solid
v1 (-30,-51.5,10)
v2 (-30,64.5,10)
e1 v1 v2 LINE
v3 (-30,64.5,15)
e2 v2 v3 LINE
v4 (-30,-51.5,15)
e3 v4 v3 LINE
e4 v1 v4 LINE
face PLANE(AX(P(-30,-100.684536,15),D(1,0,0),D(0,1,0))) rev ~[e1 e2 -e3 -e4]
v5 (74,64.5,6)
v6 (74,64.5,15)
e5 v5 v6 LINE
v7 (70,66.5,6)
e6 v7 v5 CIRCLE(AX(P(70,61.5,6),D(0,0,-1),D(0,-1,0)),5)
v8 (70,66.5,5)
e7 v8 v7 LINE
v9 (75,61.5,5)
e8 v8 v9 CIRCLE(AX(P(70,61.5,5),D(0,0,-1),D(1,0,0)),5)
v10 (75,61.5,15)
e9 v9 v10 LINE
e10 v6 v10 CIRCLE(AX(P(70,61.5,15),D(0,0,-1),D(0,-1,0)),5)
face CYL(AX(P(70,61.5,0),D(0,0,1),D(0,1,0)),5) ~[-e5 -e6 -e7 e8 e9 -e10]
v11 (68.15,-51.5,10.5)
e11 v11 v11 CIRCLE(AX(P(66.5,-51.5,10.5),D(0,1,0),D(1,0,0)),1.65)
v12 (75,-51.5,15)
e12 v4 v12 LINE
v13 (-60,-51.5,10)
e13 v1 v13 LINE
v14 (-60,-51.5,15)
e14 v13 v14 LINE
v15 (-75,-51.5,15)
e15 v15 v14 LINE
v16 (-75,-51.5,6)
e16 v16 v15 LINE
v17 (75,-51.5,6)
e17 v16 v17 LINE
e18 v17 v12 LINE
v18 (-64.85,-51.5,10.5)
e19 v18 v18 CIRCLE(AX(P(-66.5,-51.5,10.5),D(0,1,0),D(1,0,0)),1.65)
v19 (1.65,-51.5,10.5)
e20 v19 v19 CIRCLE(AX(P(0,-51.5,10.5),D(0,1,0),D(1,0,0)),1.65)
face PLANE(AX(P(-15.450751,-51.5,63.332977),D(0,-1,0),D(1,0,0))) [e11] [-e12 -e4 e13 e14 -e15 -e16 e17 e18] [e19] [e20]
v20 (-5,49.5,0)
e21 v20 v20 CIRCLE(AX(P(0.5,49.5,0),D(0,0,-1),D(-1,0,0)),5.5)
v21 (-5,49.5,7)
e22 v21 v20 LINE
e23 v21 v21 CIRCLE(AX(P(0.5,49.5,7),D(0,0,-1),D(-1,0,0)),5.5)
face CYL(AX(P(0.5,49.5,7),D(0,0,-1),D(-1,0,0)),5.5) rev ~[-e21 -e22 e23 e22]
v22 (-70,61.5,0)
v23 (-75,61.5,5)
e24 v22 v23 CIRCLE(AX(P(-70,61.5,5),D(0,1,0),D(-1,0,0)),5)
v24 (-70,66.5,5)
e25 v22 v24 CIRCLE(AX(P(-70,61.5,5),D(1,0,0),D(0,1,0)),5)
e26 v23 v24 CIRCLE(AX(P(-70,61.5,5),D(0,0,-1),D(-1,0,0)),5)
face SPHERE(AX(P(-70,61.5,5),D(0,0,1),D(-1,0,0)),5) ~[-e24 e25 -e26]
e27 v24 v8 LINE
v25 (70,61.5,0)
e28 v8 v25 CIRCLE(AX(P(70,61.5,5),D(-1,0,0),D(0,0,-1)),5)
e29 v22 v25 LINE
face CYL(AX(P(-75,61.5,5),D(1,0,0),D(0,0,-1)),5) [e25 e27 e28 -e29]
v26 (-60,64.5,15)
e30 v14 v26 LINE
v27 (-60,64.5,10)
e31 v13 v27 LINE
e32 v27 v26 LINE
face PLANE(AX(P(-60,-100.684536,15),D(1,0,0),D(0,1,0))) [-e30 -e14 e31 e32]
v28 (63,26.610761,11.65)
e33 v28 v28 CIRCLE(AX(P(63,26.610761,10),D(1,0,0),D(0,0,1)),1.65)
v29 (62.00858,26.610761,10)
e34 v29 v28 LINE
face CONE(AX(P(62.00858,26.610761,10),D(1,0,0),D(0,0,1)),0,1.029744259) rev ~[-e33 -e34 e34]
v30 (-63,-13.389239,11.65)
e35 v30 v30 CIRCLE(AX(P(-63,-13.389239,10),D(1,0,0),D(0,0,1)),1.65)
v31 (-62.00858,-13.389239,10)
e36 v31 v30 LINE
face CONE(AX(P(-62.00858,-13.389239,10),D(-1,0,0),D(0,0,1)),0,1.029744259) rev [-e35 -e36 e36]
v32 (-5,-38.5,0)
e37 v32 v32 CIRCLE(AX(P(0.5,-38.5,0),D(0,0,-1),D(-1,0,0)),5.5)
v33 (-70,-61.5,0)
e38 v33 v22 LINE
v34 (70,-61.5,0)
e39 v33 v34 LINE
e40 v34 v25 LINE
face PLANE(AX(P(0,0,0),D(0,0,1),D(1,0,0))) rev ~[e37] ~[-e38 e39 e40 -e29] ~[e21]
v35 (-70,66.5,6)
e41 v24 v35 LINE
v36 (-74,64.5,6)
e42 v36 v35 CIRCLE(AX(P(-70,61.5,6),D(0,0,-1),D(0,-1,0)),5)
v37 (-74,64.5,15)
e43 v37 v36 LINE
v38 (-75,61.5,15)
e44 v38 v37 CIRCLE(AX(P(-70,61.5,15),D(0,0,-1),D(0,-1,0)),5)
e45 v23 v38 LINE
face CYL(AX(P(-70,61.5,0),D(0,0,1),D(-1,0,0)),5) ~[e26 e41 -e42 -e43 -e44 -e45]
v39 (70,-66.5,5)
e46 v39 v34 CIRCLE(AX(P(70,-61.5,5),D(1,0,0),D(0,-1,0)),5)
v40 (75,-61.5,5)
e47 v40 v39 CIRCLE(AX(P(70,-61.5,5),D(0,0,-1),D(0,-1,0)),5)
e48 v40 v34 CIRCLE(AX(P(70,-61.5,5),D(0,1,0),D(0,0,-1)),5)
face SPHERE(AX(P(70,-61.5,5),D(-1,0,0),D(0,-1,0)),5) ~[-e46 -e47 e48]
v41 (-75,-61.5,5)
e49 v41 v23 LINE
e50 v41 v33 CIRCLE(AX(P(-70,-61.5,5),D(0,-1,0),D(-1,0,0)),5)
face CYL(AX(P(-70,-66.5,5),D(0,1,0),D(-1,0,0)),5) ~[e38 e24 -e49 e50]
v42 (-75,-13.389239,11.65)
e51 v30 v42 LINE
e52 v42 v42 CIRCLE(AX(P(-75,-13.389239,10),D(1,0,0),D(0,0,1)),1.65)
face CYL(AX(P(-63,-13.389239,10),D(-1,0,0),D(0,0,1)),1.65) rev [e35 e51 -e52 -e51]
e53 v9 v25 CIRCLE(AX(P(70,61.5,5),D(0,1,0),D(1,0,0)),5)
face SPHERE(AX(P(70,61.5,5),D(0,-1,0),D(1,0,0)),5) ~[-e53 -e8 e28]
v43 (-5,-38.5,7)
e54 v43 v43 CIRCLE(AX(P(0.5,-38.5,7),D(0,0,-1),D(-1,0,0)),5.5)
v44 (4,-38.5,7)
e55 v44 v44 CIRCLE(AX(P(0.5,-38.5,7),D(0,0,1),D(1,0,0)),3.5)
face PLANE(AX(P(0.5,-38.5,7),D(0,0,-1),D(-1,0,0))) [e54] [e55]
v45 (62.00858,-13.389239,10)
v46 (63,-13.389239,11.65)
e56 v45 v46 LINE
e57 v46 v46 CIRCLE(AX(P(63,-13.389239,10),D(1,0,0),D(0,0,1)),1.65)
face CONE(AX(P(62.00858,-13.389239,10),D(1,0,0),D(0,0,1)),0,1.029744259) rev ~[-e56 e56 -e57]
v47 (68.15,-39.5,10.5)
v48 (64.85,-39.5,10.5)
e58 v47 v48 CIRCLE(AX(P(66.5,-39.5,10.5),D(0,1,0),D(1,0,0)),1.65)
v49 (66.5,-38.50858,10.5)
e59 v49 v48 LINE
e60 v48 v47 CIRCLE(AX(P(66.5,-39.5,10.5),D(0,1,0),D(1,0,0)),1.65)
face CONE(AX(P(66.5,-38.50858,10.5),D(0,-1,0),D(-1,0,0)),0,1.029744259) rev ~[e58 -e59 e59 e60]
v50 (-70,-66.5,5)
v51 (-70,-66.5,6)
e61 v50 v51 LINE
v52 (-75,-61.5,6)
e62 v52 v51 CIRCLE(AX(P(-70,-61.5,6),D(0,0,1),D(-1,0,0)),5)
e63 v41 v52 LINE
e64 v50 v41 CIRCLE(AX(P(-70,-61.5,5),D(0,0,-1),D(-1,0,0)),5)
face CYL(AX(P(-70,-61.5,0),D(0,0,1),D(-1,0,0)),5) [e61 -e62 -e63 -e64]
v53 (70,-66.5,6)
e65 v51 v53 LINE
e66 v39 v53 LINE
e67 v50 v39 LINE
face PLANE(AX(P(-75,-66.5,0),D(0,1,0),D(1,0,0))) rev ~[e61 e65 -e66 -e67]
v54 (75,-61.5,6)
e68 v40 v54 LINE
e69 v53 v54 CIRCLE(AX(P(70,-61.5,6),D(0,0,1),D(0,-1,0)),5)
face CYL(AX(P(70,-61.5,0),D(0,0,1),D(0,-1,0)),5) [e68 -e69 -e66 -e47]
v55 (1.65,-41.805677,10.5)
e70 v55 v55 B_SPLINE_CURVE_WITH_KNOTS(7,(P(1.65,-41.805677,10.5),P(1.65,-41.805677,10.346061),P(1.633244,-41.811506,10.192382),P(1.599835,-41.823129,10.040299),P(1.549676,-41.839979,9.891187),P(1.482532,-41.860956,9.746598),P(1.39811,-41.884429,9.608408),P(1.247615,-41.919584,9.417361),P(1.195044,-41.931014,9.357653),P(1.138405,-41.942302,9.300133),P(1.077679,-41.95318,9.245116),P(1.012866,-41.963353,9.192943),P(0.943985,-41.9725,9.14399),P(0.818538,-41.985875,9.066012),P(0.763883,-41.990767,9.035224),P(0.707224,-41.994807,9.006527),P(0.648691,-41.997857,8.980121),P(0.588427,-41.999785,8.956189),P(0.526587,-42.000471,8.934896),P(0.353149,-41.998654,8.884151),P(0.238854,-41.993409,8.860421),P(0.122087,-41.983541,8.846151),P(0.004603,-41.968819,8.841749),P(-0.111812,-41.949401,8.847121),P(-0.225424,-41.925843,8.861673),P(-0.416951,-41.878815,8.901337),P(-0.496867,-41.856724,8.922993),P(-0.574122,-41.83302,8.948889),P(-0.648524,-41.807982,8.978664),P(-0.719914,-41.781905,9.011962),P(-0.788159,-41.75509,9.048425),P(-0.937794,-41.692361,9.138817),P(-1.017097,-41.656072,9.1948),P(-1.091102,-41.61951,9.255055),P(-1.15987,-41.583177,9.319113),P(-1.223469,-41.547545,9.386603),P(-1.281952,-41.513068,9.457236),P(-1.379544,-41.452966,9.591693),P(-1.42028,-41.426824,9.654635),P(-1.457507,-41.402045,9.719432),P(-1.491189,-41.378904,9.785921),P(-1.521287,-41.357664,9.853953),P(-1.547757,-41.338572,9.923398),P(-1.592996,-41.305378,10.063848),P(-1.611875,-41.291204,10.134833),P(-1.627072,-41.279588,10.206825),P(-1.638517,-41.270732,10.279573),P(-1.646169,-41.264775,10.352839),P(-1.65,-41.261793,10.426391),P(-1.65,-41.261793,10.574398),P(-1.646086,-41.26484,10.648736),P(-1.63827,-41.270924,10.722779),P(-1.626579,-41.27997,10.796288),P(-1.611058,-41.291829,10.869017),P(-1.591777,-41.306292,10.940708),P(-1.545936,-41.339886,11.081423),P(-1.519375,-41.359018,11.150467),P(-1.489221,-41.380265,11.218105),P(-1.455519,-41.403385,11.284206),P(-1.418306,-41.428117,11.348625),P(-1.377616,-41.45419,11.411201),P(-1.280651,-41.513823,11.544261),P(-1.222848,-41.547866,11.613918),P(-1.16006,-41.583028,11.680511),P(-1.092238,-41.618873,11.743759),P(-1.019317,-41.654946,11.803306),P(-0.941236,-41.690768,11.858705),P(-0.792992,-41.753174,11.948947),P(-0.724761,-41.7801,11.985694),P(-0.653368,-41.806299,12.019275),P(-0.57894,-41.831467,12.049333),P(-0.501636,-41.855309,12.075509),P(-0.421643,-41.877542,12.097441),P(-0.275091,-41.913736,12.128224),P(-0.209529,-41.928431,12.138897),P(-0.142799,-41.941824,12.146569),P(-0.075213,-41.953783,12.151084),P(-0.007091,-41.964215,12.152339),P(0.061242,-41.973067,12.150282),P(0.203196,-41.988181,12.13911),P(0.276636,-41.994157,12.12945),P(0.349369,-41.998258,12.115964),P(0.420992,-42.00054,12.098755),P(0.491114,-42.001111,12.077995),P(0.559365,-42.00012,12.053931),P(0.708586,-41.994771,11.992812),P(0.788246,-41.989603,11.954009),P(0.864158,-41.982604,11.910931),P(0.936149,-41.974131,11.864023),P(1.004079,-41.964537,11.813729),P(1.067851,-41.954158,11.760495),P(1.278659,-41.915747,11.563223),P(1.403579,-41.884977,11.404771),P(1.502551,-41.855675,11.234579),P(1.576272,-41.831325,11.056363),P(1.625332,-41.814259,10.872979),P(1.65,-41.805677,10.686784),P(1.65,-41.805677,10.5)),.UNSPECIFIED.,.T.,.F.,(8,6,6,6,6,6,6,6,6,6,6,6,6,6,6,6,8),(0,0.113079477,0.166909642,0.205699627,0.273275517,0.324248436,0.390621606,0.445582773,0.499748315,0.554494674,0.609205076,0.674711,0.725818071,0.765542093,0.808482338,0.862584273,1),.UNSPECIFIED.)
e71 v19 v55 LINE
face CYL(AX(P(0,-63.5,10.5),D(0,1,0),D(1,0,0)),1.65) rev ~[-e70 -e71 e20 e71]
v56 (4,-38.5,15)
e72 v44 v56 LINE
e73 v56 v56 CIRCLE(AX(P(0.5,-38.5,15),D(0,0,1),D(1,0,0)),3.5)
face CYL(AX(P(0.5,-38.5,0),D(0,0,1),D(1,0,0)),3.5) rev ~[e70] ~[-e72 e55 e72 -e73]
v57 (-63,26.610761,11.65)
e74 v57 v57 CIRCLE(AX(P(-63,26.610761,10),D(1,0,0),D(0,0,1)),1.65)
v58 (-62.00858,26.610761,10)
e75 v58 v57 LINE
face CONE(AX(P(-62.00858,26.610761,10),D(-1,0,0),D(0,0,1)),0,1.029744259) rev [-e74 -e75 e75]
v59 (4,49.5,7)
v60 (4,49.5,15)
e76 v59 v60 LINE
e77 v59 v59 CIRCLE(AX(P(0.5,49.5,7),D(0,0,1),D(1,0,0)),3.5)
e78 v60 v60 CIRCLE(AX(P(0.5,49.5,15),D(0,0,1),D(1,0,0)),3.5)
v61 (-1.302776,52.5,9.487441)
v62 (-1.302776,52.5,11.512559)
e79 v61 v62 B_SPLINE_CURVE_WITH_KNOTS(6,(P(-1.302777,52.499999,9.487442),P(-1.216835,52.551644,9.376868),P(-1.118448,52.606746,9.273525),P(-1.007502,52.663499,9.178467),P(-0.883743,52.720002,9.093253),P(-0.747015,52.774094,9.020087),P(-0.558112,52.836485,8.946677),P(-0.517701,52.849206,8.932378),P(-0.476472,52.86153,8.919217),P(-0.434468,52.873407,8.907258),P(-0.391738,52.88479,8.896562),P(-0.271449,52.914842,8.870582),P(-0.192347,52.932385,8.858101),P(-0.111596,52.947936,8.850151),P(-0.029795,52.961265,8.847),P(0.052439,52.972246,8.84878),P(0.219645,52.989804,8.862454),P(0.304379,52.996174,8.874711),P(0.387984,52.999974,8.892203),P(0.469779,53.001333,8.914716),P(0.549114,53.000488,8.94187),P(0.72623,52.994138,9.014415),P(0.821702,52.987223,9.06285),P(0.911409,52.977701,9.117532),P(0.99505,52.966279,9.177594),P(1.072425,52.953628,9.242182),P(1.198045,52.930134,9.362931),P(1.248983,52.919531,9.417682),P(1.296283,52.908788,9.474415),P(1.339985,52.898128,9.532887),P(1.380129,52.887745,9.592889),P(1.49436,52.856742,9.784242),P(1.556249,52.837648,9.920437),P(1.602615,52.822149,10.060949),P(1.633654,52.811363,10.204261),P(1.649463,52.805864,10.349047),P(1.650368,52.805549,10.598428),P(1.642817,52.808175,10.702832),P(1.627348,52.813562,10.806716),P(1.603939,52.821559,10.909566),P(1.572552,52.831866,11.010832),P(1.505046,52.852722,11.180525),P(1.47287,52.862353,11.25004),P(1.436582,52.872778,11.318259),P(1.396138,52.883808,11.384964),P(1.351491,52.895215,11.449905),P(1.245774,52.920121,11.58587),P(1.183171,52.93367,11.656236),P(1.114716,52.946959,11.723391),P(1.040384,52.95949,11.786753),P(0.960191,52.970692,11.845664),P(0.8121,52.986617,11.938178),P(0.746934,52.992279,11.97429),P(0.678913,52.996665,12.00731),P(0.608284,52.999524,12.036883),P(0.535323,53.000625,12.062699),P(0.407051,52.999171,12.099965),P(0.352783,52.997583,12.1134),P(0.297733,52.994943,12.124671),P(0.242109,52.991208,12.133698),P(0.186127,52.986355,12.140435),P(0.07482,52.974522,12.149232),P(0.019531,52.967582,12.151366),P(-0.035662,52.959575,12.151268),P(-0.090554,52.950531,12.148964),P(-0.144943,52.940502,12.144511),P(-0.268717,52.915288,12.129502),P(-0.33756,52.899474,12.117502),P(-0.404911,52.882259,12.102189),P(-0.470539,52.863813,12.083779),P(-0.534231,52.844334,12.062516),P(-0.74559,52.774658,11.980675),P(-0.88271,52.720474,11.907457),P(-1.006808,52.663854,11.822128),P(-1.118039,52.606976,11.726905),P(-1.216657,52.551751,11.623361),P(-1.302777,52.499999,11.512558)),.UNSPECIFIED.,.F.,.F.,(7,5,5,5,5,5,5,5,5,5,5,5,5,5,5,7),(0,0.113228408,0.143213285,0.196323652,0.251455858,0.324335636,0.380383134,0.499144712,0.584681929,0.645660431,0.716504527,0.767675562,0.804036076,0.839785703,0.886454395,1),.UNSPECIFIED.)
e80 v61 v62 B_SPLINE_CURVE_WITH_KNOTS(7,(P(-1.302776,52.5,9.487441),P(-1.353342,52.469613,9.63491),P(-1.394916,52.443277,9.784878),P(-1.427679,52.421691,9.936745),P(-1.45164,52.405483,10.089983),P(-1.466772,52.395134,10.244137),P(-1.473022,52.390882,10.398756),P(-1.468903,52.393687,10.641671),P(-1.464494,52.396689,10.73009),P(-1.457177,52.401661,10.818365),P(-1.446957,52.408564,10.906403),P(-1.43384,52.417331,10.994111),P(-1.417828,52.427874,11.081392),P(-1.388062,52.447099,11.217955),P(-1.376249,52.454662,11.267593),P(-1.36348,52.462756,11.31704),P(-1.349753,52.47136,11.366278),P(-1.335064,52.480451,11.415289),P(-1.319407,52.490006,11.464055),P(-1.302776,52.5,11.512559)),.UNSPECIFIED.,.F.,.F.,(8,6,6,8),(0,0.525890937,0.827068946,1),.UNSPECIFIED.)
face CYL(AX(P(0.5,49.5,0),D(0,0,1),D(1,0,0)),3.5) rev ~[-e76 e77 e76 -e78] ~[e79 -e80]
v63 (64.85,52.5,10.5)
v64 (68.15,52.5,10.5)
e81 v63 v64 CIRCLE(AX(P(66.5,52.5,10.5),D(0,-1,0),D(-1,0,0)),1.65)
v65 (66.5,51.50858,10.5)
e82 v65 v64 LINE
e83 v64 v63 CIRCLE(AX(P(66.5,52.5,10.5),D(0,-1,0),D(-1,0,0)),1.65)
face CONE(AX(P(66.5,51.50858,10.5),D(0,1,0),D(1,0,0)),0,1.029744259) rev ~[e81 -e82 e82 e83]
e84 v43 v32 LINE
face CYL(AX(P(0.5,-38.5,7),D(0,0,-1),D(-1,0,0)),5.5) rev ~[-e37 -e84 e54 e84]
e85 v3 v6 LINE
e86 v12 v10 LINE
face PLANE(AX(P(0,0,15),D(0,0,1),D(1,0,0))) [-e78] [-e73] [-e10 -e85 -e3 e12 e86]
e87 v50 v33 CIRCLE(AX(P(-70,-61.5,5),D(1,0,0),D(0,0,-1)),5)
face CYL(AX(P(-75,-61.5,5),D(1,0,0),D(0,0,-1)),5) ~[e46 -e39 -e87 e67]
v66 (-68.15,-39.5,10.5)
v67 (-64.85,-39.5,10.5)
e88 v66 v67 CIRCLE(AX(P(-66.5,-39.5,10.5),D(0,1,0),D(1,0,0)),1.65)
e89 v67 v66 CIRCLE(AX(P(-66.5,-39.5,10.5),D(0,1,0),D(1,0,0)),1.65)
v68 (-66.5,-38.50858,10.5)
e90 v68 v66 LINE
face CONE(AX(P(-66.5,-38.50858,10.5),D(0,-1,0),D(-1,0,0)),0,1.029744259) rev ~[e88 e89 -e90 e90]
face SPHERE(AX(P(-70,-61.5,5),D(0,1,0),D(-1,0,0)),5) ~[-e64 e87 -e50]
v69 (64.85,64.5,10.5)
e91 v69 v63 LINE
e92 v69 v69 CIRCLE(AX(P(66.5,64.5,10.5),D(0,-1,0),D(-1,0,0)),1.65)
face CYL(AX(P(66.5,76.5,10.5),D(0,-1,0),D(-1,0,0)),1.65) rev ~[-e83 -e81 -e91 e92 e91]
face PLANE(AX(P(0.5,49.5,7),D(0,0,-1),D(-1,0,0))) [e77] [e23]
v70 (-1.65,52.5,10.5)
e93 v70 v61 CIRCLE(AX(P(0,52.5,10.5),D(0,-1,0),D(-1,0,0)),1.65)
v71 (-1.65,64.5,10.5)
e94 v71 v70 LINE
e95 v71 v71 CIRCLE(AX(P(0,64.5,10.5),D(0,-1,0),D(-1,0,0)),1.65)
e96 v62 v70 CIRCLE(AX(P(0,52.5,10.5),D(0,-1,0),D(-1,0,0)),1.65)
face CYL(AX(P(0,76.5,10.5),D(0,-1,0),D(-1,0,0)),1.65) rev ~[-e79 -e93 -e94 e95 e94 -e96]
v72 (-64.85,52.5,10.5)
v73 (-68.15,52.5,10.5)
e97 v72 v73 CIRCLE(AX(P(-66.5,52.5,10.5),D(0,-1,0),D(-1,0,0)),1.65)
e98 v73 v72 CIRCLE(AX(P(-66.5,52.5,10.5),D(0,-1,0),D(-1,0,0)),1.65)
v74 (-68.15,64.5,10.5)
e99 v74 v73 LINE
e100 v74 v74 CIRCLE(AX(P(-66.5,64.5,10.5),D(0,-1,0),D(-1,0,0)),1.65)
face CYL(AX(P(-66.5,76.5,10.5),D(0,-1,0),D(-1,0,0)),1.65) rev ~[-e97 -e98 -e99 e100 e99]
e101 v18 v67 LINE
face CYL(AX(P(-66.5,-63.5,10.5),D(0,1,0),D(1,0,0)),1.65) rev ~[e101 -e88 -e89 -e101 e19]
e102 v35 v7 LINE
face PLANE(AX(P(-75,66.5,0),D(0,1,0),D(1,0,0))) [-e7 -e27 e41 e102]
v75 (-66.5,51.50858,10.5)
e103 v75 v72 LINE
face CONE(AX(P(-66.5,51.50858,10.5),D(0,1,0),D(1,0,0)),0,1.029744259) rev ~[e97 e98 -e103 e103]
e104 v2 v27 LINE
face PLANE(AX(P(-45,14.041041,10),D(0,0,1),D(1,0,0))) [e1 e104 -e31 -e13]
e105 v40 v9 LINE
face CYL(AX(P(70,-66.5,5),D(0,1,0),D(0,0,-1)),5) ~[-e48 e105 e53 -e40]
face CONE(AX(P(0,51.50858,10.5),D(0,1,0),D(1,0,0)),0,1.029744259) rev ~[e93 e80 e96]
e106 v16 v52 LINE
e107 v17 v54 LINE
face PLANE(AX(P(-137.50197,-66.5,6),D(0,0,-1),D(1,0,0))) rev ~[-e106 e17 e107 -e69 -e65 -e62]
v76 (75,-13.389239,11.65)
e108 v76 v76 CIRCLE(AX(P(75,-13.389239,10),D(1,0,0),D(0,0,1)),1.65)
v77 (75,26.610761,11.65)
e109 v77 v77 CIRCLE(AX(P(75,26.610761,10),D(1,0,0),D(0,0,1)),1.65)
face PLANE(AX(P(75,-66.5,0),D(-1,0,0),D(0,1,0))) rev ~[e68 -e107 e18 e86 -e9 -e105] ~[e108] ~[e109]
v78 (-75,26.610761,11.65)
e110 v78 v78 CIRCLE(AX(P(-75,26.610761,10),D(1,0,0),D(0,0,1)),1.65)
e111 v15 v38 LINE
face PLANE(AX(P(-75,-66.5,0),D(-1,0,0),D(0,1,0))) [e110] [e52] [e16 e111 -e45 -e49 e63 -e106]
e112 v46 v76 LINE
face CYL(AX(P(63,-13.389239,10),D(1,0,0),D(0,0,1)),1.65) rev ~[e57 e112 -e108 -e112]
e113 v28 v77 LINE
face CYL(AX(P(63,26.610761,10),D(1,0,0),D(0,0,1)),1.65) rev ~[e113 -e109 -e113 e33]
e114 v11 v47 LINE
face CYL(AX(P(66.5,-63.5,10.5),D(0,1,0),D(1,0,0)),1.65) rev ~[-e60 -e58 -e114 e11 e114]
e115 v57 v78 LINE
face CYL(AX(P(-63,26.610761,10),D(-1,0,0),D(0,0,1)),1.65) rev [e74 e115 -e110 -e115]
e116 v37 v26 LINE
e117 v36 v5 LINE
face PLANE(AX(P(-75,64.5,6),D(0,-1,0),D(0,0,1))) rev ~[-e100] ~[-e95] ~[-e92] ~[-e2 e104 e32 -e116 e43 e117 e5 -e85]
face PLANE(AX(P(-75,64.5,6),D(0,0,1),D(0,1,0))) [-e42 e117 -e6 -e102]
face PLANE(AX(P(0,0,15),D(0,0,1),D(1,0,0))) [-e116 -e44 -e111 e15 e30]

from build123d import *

# Parameters (mm, degrees)
SKETCH_1_W                  = 150
SKETCH_1_H                  = 133
EXTRUDE_1_DEPTH             = 15
SKETCH_2_W                  = 23.680798508
SKETCH_2_H                  = 30.226028772
CUT_EXTRUDE_1_DEPTH         = 165.764225486
FILLET_2_R                  = 5
HOLE_WIZARD_2_D             = 7
HOLE_WIZARD_2_CBORE_D       = 11
HOLE_WIZARD_2_CBORE_DEPTH   = 7
SKETCH_19_W                 = 244.102436516
SKETCH_19_H                 = 114.665953459
CUT_EXTRUDE_7_DEPTH         = 15
SKETCH_29_W                 = 30
SKETCH_29_H                 = 229.451153657
CUT_EXTRUDE_11_DEPTH        = 5
HOLE_WIZARD_M4_1_D          = 3.3
HOLE_WIZARD_M4_1_DEPTH      = 12
HOLE_WIZARD_M4_1_TIP        = 0.991420021
HOLE_WIZARD_M4_2_D          = 3.3
HOLE_WIZARD_M4_2_DEPTH      = 12
HOLE_WIZARD_M4_2_TIP        = 0.991420021
HOLE_WIZARD_M4_3_AT_2_COUNT = 2
HOLE_WIZARD_M4_3_AT_2_PITCH = 40


with BuildPart() as part:
    # 草图1 → 凸台-拉伸1 (new body)
    with BuildSketch(Plane.XY):
        Rectangle(SKETCH_1_W, SKETCH_1_H)
    extrude(amount=EXTRUDE_1_DEPTH)

    # 草图2 → 切除-拉伸1 (cut, through all)
    with BuildSketch(Plane.ZY.offset(75)):
        with Locations((17.840399254, 79.613014386)):
            Rectangle(SKETCH_2_W, SKETCH_2_H)
    extrude(amount=-CUT_EXTRUDE_1_DEPTH, mode=Mode.SUBTRACT)

    # 圆角2
    fillet_2_edges = [part.edges().sort_by_distance(p)[0] for p in [
        (-75, 66.5, 3),
        (-75, 0, 0),
        (-75, -66.5, 7.5),
        (0, -66.5, 0),
        (75, -66.5, 7.5),
        (75, 0, 0),
        (75, 66.5, 3),
        (0, 66.5, 0),
    ]]
    fillet(fillet_2_edges, radius=FILLET_2_R)

    # 打孔尺寸(%根据)开槽圆柱头螺钉的类型2 (through all)
    with Locations(Plane(origin=(0, 0, 0), x_dir=(-1, 0, 0), z_dir=(0, 0, -1))):
        with Locations((-0.5, 49.5), (-0.5, -38.5)):
            CounterBoreHole(HOLE_WIZARD_2_D / 2, HOLE_WIZARD_2_CBORE_D / 2, HOLE_WIZARD_2_CBORE_DEPTH)

    # 草图19 → 切除-拉伸7 (cut)
    with BuildSketch(Plane.XZ.offset(66.5)):
        with Locations((-15.450751356, 63.33297673)):
            Rectangle(SKETCH_19_W, SKETCH_19_H)
    extrude(amount=-CUT_EXTRUDE_7_DEPTH, mode=Mode.SUBTRACT)

    # 草图29 → 切除-拉伸11 (cut)
    with BuildSketch(Plane.XY.offset(15)):
        with Locations((-45, 14.041040746)):
            Rectangle(SKETCH_29_W, SKETCH_29_H)
    extrude(amount=-CUT_EXTRUDE_11_DEPTH, mode=Mode.SUBTRACT)

    # M4 螺纹孔1
    with Locations(Plane(origin=(0, -51.5, 0), x_dir=(-1, 0, 0), z_dir=(0, -1, 0))):
        with Locations((66.5, -10.5), (-66.5, -10.5), (0, -10.5)):
            Hole(HOLE_WIZARD_M4_1_D / 2, depth=HOLE_WIZARD_M4_1_DEPTH)
            with Locations((0, 0, -(HOLE_WIZARD_M4_1_DEPTH + HOLE_WIZARD_M4_1_TIP / 2))):  # 118° drill point
                Cone(0, HOLE_WIZARD_M4_1_D / 2, HOLE_WIZARD_M4_1_TIP, mode=Mode.SUBTRACT)

    # M4 螺纹孔2
    with Locations(Plane(origin=(0, 64.5, 0), x_dir=(1, 0, 0), z_dir=(0, 1, 0))):
        with Locations((-66.5, -10.5), (66.5, -10.5), (0, -10.5)):
            Hole(HOLE_WIZARD_M4_2_D / 2, depth=HOLE_WIZARD_M4_2_DEPTH)
            with Locations((0, 0, -(HOLE_WIZARD_M4_2_DEPTH + HOLE_WIZARD_M4_2_TIP / 2))):  # 118° drill point
                Cone(0, HOLE_WIZARD_M4_2_D / 2, HOLE_WIZARD_M4_2_TIP, mode=Mode.SUBTRACT)

    # 草图37 → M4 螺纹孔3 (revolve, cut)
    with BuildSketch(Plane(origin=(-75, 26.61076125, 10), x_dir=(0, 0, 1), z_dir=(0, 1, 0))):
        Polygon((0, 0), (0, 12.991420021), (1.65, 12), (1.65, 0), align=None)
    hole_wizard_m4_3 = revolve(axis=Axis((-81.35, 26.61076125, 10), (1, 0, 0)), mode=Mode.SUBTRACT)

    # M4 螺纹孔3 at 2: M4 螺纹孔3 ×2
    with Locations(*[(0, -i * HOLE_WIZARD_M4_3_AT_2_PITCH, 0) for i in range(1, HOLE_WIZARD_M4_3_AT_2_COUNT)]):
        add(hole_wizard_m4_3, mode=Mode.SUBTRACT)

    # 镜向1: M4 螺纹孔3 across plane
    add(hole_wizard_m4_3.mirror(Plane(origin=(0, 0, 0), x_dir=(0, 0, 1), z_dir=(1, 0, 0))), mode=Mode.SUBTRACT)

    # 镜向1 copy 1 sketch → 镜向1 copy 1 (revolve, cut)
    with BuildSketch(Plane(origin=(75, -13.38923875, 10), x_dir=(0, 0, 1), z_dir=(0, 1, 0))):
        Polygon((0, 0), (0, -12.991420021), (1.65, -12), (1.65, 0), align=None)
    revolve(axis=Axis((81.35, -13.38923875, 10), (1, 0, 0)), mode=Mode.SUBTRACT)


solid = part.part
